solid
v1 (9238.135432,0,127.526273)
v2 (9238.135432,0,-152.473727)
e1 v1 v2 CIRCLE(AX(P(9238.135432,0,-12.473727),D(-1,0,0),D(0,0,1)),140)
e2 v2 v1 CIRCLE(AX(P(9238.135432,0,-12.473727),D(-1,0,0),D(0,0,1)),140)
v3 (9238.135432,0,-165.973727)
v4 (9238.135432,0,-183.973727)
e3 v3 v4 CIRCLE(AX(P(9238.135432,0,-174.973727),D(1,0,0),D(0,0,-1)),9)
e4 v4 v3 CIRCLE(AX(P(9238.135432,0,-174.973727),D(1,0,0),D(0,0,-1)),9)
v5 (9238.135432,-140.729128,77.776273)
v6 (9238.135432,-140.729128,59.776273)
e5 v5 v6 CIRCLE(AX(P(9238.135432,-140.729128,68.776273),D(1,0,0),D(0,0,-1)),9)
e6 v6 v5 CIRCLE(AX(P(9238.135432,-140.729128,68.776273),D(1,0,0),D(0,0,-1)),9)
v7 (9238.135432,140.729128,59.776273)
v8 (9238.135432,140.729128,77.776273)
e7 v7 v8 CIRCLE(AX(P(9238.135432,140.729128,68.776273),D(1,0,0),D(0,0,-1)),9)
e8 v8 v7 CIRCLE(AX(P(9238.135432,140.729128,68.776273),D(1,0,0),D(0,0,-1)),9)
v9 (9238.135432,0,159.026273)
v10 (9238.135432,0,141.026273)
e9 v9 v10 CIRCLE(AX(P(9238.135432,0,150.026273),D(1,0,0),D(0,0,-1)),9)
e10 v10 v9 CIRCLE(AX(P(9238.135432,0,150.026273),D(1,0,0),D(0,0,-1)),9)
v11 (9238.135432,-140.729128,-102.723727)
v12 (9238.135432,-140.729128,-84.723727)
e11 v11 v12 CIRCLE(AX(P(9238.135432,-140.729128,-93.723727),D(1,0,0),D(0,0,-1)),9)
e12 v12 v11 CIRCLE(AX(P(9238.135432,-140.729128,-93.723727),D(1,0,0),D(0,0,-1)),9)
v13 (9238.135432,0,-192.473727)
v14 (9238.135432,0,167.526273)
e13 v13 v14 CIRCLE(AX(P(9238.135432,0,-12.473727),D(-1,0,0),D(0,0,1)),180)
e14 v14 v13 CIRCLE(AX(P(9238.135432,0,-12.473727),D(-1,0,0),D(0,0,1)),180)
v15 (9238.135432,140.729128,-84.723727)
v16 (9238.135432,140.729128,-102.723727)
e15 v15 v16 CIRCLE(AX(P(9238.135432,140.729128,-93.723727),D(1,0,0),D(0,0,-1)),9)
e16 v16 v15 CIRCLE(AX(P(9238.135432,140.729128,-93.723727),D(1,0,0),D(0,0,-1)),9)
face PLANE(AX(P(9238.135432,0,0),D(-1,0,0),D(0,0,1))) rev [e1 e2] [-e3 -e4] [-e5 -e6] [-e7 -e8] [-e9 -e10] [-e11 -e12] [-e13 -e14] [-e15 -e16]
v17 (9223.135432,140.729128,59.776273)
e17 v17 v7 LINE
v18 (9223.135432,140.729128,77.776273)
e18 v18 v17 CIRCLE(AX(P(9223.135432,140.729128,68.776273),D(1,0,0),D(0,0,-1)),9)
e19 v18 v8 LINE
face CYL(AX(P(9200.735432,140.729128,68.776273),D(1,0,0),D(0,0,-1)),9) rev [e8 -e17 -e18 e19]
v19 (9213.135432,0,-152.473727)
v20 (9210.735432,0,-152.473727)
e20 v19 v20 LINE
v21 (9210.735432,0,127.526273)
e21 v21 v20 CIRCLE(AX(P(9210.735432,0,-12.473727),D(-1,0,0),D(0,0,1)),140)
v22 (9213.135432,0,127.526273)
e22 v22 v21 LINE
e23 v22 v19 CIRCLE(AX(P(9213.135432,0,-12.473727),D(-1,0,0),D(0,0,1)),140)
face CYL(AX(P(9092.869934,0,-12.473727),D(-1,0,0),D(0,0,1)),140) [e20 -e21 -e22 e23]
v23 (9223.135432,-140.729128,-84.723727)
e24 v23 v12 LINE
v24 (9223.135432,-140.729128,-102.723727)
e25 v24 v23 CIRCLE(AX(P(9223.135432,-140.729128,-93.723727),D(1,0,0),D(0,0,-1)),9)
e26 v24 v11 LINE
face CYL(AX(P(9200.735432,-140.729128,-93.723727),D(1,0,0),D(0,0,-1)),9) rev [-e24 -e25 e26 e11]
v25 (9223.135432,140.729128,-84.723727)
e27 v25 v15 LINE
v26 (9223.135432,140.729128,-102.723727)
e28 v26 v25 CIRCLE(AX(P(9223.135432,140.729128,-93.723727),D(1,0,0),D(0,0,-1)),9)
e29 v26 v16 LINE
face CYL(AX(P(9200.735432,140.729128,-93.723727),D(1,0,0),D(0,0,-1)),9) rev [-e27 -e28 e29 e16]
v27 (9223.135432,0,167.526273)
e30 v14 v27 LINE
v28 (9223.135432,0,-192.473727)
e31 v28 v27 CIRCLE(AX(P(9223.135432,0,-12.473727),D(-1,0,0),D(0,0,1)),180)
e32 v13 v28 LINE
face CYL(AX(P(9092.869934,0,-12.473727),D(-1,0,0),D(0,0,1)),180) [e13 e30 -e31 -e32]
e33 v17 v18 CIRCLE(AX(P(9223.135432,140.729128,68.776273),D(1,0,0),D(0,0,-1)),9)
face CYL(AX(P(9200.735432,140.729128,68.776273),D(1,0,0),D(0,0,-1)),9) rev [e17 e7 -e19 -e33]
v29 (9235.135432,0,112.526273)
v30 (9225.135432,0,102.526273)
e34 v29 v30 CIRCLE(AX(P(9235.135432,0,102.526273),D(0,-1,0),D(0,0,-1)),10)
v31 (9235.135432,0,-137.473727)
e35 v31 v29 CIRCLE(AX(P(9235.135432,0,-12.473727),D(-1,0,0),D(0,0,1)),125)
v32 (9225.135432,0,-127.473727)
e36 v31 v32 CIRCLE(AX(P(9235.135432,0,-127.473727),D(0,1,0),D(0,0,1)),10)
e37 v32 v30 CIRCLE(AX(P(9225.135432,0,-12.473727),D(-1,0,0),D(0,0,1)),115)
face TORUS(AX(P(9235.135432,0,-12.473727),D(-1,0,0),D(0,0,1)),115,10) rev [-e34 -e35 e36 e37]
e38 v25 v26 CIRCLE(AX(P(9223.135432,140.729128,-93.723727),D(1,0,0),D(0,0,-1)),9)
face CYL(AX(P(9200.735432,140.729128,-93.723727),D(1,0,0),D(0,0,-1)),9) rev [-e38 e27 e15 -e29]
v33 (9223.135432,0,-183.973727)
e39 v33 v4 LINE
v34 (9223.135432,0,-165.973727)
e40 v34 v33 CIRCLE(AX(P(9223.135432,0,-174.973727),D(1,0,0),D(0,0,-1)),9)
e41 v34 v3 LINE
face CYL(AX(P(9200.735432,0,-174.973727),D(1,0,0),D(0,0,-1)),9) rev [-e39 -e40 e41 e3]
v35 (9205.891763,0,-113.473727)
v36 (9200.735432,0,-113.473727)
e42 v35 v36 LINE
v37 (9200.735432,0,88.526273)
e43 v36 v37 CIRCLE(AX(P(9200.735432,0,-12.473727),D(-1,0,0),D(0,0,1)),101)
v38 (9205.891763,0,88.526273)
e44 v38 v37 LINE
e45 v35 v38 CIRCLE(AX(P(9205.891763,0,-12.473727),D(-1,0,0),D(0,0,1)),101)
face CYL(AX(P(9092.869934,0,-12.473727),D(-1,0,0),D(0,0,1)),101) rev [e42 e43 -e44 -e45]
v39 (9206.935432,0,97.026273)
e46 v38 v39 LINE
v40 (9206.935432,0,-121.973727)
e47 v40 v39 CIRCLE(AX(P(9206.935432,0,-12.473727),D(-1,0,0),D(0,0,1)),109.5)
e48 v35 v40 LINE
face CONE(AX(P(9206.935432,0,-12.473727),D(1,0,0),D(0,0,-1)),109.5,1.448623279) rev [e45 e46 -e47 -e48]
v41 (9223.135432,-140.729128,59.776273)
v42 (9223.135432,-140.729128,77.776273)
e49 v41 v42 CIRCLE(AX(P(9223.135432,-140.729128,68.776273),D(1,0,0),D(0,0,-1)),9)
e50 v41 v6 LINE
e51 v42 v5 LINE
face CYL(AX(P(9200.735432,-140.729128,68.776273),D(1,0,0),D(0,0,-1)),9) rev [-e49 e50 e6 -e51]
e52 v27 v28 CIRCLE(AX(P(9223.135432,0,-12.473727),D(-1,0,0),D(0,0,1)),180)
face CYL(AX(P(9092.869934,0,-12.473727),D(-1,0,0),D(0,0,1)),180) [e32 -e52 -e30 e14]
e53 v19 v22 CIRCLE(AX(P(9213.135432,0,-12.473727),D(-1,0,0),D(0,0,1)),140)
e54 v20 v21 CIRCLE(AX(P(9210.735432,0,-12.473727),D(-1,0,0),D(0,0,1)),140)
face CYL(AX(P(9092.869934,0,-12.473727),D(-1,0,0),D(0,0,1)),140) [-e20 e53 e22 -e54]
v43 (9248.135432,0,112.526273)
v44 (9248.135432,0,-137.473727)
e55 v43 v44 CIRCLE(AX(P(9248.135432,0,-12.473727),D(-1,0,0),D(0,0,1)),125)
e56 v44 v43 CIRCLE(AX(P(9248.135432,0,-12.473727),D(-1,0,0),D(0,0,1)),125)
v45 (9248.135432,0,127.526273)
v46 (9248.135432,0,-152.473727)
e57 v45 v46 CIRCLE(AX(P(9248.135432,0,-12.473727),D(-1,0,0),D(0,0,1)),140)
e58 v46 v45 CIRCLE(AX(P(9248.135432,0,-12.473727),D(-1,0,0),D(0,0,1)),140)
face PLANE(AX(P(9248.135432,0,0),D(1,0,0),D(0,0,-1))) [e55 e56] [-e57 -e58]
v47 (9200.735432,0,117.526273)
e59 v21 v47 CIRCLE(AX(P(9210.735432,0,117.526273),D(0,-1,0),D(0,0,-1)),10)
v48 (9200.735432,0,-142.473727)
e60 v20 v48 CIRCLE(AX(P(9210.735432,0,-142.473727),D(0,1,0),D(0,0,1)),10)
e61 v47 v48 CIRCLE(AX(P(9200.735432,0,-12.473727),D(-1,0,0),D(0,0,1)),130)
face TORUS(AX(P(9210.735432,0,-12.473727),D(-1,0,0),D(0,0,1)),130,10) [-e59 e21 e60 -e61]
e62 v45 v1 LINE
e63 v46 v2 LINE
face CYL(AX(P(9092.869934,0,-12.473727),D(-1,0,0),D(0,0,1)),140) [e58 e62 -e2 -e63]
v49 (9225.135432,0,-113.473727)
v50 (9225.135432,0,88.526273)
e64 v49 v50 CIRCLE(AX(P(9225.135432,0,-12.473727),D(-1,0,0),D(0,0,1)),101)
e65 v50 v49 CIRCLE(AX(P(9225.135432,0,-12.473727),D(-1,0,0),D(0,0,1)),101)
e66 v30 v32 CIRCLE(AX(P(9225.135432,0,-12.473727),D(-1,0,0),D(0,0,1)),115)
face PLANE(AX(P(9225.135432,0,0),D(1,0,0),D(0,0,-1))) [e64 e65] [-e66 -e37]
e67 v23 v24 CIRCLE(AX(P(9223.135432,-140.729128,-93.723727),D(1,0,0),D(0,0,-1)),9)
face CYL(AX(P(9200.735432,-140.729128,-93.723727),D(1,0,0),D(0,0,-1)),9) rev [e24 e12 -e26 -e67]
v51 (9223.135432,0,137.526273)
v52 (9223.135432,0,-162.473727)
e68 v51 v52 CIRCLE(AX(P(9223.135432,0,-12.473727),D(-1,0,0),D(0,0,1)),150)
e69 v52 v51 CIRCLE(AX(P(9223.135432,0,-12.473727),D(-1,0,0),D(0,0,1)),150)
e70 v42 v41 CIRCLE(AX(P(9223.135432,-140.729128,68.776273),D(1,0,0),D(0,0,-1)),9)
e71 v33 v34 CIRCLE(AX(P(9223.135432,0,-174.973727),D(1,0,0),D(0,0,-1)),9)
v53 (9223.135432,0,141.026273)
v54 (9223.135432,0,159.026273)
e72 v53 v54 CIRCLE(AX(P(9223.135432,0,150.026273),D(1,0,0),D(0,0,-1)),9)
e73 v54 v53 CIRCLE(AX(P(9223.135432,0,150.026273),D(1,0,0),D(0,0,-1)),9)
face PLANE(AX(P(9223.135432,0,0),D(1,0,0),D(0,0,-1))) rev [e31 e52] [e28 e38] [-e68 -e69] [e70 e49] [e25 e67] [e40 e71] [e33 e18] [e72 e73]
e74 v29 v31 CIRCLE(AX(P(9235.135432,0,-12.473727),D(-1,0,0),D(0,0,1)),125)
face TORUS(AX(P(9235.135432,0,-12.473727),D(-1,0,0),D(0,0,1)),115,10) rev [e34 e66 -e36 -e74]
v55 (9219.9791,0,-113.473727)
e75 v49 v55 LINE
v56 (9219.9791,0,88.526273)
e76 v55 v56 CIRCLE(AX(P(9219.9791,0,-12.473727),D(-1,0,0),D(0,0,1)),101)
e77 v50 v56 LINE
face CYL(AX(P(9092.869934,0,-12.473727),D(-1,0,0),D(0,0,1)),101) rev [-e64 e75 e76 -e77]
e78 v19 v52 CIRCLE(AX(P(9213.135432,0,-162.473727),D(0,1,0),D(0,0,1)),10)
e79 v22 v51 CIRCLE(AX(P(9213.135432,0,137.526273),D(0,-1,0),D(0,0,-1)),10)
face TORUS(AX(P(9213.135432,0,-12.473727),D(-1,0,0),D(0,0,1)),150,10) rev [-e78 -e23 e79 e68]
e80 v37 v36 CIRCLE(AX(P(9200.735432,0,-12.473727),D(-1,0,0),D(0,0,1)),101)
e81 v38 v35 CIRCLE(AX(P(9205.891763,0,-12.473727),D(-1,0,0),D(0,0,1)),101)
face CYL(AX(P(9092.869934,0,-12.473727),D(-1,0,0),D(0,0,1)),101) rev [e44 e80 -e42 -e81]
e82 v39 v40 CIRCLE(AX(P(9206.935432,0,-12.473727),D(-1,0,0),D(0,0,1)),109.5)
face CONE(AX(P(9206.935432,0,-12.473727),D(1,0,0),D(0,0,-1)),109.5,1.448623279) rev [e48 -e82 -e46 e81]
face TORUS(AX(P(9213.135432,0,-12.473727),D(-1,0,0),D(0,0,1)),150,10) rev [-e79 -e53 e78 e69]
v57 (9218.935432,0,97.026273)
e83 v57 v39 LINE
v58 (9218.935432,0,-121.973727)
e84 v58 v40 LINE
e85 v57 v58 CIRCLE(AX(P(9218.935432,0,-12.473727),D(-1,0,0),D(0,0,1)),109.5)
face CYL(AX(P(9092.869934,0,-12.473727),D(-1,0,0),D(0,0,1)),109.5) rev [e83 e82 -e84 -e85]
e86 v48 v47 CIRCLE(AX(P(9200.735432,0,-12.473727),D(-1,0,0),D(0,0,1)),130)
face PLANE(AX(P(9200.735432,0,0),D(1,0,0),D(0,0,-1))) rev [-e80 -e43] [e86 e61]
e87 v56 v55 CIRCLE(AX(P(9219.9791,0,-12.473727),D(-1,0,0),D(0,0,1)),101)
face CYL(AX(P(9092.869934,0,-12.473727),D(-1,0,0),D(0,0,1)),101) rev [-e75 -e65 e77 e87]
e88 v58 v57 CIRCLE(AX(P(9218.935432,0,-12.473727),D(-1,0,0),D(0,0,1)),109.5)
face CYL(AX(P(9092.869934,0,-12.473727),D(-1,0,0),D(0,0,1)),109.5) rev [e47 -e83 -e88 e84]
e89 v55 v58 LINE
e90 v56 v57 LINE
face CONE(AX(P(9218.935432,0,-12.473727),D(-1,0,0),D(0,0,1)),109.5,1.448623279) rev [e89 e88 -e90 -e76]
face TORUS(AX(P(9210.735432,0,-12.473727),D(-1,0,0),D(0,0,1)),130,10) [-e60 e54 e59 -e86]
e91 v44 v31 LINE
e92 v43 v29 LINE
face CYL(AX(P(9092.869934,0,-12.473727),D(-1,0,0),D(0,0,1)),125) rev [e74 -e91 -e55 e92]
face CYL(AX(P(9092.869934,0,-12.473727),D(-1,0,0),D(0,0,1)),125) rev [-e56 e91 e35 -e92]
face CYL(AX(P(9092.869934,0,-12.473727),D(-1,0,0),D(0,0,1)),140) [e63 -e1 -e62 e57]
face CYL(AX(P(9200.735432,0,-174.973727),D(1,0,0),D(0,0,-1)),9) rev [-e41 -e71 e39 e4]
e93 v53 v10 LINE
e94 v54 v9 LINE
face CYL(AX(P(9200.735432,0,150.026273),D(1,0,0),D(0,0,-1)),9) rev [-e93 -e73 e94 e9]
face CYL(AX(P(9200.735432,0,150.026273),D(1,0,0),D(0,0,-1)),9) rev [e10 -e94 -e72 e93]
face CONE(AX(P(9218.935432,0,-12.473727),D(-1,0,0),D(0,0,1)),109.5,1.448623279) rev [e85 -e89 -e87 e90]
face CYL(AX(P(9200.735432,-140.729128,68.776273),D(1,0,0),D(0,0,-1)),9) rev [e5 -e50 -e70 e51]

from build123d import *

# Parameters (mm, degrees)
SKETCH2_R          = 9
CUT_EXTRUDE1_DEPTH = 267.167044388


with BuildPart() as part:
    # Sketch1 → Revolve1 (revolve)
    with BuildSketch(Plane(origin=(0, 0, 0), x_dir=(1, 0, 0), z_dir=(0, 1, 0)), mode=Mode.PRIVATE) as revolve1_sk:
        with BuildLine():
            ThreePointArc((9235.135431533, 137.473726826), (9228.064363722, 134.544794638), (9225.135431533, 127.473726826))
            Line((9225.135431533, 127.473726826), (9225.135431533, 113.473726826))
            Line((9225.135431533, 113.473726826), (9219.979100301, 113.473726826))
            Line((9219.979100301, 113.473726826), (9218.935431533, 121.973726826))
            Line((9218.935431533, 121.973726826), (9206.935431533, 121.973726826))
            Line((9206.935431533, 121.973726826), (9205.891762766, 113.473726826))
            Line((9205.891762766, 113.473726826), (9200.735431533, 113.473726826))
            Line((9200.735431533, 113.473726826), (9200.735431533, 142.473726826))
            ThreePointArc((9200.735431533, 142.473726826), (9203.664363722, 149.544794638), (9210.735431533, 152.473726826))
            Line((9210.735431533, 152.473726826), (9213.135431533, 152.473726826))
            ThreePointArc((9213.135431533, 152.473726826), (9220.206499345, 155.402659014), (9223.135431533, 162.473726826))
            Line((9223.135431533, 162.473726826), (9223.135431533, 192.473726826))
            Line((9223.135431533, 192.473726826), (9238.135431533, 192.473726826))
            Line((9238.135431533, 192.473726826), (9238.135431533, 152.473726826))
            Line((9238.135431533, 152.473726826), (9248.135431533, 152.473726826))
            Line((9248.135431533, 152.473726826), (9248.135431533, 137.473726826))
            Line((9248.135431533, 137.473726826), (9235.135431533, 137.473726826))
        make_face()
    revolve(revolve1_sk.sketch.rotate(Axis((9092.86993426, 0, -12.473726826), (1, 0, 0)), 180), axis=Axis((9092.86993426, 0, -12.473726826), (1, 0, 0)))

    # Sketch2 → Cut-Extrude1 (cut, through all)
    with BuildSketch(Plane(origin=(9238.135431533, 0, 0), x_dir=(0, 0, -1), z_dir=(1, 0, 0))):
        with Locations((-68.776273174, 140.729128115)):
            Circle(SKETCH2_R)
        with Locations((93.723726826, 140.729128115)):
            Circle(SKETCH2_R)
        with Locations((174.973726826, 0)):
            Circle(SKETCH2_R)
        with Locations((93.723726826, -140.729128115)):
            Circle(SKETCH2_R)
        with Locations((-68.776273174, -140.729128115)):
            Circle(SKETCH2_R)
        with Locations((-150.026273174, 0)):
            Circle(SKETCH2_R)
    extrude(amount=-CUT_EXTRUDE1_DEPTH, mode=Mode.SUBTRACT)


solid = part.part
